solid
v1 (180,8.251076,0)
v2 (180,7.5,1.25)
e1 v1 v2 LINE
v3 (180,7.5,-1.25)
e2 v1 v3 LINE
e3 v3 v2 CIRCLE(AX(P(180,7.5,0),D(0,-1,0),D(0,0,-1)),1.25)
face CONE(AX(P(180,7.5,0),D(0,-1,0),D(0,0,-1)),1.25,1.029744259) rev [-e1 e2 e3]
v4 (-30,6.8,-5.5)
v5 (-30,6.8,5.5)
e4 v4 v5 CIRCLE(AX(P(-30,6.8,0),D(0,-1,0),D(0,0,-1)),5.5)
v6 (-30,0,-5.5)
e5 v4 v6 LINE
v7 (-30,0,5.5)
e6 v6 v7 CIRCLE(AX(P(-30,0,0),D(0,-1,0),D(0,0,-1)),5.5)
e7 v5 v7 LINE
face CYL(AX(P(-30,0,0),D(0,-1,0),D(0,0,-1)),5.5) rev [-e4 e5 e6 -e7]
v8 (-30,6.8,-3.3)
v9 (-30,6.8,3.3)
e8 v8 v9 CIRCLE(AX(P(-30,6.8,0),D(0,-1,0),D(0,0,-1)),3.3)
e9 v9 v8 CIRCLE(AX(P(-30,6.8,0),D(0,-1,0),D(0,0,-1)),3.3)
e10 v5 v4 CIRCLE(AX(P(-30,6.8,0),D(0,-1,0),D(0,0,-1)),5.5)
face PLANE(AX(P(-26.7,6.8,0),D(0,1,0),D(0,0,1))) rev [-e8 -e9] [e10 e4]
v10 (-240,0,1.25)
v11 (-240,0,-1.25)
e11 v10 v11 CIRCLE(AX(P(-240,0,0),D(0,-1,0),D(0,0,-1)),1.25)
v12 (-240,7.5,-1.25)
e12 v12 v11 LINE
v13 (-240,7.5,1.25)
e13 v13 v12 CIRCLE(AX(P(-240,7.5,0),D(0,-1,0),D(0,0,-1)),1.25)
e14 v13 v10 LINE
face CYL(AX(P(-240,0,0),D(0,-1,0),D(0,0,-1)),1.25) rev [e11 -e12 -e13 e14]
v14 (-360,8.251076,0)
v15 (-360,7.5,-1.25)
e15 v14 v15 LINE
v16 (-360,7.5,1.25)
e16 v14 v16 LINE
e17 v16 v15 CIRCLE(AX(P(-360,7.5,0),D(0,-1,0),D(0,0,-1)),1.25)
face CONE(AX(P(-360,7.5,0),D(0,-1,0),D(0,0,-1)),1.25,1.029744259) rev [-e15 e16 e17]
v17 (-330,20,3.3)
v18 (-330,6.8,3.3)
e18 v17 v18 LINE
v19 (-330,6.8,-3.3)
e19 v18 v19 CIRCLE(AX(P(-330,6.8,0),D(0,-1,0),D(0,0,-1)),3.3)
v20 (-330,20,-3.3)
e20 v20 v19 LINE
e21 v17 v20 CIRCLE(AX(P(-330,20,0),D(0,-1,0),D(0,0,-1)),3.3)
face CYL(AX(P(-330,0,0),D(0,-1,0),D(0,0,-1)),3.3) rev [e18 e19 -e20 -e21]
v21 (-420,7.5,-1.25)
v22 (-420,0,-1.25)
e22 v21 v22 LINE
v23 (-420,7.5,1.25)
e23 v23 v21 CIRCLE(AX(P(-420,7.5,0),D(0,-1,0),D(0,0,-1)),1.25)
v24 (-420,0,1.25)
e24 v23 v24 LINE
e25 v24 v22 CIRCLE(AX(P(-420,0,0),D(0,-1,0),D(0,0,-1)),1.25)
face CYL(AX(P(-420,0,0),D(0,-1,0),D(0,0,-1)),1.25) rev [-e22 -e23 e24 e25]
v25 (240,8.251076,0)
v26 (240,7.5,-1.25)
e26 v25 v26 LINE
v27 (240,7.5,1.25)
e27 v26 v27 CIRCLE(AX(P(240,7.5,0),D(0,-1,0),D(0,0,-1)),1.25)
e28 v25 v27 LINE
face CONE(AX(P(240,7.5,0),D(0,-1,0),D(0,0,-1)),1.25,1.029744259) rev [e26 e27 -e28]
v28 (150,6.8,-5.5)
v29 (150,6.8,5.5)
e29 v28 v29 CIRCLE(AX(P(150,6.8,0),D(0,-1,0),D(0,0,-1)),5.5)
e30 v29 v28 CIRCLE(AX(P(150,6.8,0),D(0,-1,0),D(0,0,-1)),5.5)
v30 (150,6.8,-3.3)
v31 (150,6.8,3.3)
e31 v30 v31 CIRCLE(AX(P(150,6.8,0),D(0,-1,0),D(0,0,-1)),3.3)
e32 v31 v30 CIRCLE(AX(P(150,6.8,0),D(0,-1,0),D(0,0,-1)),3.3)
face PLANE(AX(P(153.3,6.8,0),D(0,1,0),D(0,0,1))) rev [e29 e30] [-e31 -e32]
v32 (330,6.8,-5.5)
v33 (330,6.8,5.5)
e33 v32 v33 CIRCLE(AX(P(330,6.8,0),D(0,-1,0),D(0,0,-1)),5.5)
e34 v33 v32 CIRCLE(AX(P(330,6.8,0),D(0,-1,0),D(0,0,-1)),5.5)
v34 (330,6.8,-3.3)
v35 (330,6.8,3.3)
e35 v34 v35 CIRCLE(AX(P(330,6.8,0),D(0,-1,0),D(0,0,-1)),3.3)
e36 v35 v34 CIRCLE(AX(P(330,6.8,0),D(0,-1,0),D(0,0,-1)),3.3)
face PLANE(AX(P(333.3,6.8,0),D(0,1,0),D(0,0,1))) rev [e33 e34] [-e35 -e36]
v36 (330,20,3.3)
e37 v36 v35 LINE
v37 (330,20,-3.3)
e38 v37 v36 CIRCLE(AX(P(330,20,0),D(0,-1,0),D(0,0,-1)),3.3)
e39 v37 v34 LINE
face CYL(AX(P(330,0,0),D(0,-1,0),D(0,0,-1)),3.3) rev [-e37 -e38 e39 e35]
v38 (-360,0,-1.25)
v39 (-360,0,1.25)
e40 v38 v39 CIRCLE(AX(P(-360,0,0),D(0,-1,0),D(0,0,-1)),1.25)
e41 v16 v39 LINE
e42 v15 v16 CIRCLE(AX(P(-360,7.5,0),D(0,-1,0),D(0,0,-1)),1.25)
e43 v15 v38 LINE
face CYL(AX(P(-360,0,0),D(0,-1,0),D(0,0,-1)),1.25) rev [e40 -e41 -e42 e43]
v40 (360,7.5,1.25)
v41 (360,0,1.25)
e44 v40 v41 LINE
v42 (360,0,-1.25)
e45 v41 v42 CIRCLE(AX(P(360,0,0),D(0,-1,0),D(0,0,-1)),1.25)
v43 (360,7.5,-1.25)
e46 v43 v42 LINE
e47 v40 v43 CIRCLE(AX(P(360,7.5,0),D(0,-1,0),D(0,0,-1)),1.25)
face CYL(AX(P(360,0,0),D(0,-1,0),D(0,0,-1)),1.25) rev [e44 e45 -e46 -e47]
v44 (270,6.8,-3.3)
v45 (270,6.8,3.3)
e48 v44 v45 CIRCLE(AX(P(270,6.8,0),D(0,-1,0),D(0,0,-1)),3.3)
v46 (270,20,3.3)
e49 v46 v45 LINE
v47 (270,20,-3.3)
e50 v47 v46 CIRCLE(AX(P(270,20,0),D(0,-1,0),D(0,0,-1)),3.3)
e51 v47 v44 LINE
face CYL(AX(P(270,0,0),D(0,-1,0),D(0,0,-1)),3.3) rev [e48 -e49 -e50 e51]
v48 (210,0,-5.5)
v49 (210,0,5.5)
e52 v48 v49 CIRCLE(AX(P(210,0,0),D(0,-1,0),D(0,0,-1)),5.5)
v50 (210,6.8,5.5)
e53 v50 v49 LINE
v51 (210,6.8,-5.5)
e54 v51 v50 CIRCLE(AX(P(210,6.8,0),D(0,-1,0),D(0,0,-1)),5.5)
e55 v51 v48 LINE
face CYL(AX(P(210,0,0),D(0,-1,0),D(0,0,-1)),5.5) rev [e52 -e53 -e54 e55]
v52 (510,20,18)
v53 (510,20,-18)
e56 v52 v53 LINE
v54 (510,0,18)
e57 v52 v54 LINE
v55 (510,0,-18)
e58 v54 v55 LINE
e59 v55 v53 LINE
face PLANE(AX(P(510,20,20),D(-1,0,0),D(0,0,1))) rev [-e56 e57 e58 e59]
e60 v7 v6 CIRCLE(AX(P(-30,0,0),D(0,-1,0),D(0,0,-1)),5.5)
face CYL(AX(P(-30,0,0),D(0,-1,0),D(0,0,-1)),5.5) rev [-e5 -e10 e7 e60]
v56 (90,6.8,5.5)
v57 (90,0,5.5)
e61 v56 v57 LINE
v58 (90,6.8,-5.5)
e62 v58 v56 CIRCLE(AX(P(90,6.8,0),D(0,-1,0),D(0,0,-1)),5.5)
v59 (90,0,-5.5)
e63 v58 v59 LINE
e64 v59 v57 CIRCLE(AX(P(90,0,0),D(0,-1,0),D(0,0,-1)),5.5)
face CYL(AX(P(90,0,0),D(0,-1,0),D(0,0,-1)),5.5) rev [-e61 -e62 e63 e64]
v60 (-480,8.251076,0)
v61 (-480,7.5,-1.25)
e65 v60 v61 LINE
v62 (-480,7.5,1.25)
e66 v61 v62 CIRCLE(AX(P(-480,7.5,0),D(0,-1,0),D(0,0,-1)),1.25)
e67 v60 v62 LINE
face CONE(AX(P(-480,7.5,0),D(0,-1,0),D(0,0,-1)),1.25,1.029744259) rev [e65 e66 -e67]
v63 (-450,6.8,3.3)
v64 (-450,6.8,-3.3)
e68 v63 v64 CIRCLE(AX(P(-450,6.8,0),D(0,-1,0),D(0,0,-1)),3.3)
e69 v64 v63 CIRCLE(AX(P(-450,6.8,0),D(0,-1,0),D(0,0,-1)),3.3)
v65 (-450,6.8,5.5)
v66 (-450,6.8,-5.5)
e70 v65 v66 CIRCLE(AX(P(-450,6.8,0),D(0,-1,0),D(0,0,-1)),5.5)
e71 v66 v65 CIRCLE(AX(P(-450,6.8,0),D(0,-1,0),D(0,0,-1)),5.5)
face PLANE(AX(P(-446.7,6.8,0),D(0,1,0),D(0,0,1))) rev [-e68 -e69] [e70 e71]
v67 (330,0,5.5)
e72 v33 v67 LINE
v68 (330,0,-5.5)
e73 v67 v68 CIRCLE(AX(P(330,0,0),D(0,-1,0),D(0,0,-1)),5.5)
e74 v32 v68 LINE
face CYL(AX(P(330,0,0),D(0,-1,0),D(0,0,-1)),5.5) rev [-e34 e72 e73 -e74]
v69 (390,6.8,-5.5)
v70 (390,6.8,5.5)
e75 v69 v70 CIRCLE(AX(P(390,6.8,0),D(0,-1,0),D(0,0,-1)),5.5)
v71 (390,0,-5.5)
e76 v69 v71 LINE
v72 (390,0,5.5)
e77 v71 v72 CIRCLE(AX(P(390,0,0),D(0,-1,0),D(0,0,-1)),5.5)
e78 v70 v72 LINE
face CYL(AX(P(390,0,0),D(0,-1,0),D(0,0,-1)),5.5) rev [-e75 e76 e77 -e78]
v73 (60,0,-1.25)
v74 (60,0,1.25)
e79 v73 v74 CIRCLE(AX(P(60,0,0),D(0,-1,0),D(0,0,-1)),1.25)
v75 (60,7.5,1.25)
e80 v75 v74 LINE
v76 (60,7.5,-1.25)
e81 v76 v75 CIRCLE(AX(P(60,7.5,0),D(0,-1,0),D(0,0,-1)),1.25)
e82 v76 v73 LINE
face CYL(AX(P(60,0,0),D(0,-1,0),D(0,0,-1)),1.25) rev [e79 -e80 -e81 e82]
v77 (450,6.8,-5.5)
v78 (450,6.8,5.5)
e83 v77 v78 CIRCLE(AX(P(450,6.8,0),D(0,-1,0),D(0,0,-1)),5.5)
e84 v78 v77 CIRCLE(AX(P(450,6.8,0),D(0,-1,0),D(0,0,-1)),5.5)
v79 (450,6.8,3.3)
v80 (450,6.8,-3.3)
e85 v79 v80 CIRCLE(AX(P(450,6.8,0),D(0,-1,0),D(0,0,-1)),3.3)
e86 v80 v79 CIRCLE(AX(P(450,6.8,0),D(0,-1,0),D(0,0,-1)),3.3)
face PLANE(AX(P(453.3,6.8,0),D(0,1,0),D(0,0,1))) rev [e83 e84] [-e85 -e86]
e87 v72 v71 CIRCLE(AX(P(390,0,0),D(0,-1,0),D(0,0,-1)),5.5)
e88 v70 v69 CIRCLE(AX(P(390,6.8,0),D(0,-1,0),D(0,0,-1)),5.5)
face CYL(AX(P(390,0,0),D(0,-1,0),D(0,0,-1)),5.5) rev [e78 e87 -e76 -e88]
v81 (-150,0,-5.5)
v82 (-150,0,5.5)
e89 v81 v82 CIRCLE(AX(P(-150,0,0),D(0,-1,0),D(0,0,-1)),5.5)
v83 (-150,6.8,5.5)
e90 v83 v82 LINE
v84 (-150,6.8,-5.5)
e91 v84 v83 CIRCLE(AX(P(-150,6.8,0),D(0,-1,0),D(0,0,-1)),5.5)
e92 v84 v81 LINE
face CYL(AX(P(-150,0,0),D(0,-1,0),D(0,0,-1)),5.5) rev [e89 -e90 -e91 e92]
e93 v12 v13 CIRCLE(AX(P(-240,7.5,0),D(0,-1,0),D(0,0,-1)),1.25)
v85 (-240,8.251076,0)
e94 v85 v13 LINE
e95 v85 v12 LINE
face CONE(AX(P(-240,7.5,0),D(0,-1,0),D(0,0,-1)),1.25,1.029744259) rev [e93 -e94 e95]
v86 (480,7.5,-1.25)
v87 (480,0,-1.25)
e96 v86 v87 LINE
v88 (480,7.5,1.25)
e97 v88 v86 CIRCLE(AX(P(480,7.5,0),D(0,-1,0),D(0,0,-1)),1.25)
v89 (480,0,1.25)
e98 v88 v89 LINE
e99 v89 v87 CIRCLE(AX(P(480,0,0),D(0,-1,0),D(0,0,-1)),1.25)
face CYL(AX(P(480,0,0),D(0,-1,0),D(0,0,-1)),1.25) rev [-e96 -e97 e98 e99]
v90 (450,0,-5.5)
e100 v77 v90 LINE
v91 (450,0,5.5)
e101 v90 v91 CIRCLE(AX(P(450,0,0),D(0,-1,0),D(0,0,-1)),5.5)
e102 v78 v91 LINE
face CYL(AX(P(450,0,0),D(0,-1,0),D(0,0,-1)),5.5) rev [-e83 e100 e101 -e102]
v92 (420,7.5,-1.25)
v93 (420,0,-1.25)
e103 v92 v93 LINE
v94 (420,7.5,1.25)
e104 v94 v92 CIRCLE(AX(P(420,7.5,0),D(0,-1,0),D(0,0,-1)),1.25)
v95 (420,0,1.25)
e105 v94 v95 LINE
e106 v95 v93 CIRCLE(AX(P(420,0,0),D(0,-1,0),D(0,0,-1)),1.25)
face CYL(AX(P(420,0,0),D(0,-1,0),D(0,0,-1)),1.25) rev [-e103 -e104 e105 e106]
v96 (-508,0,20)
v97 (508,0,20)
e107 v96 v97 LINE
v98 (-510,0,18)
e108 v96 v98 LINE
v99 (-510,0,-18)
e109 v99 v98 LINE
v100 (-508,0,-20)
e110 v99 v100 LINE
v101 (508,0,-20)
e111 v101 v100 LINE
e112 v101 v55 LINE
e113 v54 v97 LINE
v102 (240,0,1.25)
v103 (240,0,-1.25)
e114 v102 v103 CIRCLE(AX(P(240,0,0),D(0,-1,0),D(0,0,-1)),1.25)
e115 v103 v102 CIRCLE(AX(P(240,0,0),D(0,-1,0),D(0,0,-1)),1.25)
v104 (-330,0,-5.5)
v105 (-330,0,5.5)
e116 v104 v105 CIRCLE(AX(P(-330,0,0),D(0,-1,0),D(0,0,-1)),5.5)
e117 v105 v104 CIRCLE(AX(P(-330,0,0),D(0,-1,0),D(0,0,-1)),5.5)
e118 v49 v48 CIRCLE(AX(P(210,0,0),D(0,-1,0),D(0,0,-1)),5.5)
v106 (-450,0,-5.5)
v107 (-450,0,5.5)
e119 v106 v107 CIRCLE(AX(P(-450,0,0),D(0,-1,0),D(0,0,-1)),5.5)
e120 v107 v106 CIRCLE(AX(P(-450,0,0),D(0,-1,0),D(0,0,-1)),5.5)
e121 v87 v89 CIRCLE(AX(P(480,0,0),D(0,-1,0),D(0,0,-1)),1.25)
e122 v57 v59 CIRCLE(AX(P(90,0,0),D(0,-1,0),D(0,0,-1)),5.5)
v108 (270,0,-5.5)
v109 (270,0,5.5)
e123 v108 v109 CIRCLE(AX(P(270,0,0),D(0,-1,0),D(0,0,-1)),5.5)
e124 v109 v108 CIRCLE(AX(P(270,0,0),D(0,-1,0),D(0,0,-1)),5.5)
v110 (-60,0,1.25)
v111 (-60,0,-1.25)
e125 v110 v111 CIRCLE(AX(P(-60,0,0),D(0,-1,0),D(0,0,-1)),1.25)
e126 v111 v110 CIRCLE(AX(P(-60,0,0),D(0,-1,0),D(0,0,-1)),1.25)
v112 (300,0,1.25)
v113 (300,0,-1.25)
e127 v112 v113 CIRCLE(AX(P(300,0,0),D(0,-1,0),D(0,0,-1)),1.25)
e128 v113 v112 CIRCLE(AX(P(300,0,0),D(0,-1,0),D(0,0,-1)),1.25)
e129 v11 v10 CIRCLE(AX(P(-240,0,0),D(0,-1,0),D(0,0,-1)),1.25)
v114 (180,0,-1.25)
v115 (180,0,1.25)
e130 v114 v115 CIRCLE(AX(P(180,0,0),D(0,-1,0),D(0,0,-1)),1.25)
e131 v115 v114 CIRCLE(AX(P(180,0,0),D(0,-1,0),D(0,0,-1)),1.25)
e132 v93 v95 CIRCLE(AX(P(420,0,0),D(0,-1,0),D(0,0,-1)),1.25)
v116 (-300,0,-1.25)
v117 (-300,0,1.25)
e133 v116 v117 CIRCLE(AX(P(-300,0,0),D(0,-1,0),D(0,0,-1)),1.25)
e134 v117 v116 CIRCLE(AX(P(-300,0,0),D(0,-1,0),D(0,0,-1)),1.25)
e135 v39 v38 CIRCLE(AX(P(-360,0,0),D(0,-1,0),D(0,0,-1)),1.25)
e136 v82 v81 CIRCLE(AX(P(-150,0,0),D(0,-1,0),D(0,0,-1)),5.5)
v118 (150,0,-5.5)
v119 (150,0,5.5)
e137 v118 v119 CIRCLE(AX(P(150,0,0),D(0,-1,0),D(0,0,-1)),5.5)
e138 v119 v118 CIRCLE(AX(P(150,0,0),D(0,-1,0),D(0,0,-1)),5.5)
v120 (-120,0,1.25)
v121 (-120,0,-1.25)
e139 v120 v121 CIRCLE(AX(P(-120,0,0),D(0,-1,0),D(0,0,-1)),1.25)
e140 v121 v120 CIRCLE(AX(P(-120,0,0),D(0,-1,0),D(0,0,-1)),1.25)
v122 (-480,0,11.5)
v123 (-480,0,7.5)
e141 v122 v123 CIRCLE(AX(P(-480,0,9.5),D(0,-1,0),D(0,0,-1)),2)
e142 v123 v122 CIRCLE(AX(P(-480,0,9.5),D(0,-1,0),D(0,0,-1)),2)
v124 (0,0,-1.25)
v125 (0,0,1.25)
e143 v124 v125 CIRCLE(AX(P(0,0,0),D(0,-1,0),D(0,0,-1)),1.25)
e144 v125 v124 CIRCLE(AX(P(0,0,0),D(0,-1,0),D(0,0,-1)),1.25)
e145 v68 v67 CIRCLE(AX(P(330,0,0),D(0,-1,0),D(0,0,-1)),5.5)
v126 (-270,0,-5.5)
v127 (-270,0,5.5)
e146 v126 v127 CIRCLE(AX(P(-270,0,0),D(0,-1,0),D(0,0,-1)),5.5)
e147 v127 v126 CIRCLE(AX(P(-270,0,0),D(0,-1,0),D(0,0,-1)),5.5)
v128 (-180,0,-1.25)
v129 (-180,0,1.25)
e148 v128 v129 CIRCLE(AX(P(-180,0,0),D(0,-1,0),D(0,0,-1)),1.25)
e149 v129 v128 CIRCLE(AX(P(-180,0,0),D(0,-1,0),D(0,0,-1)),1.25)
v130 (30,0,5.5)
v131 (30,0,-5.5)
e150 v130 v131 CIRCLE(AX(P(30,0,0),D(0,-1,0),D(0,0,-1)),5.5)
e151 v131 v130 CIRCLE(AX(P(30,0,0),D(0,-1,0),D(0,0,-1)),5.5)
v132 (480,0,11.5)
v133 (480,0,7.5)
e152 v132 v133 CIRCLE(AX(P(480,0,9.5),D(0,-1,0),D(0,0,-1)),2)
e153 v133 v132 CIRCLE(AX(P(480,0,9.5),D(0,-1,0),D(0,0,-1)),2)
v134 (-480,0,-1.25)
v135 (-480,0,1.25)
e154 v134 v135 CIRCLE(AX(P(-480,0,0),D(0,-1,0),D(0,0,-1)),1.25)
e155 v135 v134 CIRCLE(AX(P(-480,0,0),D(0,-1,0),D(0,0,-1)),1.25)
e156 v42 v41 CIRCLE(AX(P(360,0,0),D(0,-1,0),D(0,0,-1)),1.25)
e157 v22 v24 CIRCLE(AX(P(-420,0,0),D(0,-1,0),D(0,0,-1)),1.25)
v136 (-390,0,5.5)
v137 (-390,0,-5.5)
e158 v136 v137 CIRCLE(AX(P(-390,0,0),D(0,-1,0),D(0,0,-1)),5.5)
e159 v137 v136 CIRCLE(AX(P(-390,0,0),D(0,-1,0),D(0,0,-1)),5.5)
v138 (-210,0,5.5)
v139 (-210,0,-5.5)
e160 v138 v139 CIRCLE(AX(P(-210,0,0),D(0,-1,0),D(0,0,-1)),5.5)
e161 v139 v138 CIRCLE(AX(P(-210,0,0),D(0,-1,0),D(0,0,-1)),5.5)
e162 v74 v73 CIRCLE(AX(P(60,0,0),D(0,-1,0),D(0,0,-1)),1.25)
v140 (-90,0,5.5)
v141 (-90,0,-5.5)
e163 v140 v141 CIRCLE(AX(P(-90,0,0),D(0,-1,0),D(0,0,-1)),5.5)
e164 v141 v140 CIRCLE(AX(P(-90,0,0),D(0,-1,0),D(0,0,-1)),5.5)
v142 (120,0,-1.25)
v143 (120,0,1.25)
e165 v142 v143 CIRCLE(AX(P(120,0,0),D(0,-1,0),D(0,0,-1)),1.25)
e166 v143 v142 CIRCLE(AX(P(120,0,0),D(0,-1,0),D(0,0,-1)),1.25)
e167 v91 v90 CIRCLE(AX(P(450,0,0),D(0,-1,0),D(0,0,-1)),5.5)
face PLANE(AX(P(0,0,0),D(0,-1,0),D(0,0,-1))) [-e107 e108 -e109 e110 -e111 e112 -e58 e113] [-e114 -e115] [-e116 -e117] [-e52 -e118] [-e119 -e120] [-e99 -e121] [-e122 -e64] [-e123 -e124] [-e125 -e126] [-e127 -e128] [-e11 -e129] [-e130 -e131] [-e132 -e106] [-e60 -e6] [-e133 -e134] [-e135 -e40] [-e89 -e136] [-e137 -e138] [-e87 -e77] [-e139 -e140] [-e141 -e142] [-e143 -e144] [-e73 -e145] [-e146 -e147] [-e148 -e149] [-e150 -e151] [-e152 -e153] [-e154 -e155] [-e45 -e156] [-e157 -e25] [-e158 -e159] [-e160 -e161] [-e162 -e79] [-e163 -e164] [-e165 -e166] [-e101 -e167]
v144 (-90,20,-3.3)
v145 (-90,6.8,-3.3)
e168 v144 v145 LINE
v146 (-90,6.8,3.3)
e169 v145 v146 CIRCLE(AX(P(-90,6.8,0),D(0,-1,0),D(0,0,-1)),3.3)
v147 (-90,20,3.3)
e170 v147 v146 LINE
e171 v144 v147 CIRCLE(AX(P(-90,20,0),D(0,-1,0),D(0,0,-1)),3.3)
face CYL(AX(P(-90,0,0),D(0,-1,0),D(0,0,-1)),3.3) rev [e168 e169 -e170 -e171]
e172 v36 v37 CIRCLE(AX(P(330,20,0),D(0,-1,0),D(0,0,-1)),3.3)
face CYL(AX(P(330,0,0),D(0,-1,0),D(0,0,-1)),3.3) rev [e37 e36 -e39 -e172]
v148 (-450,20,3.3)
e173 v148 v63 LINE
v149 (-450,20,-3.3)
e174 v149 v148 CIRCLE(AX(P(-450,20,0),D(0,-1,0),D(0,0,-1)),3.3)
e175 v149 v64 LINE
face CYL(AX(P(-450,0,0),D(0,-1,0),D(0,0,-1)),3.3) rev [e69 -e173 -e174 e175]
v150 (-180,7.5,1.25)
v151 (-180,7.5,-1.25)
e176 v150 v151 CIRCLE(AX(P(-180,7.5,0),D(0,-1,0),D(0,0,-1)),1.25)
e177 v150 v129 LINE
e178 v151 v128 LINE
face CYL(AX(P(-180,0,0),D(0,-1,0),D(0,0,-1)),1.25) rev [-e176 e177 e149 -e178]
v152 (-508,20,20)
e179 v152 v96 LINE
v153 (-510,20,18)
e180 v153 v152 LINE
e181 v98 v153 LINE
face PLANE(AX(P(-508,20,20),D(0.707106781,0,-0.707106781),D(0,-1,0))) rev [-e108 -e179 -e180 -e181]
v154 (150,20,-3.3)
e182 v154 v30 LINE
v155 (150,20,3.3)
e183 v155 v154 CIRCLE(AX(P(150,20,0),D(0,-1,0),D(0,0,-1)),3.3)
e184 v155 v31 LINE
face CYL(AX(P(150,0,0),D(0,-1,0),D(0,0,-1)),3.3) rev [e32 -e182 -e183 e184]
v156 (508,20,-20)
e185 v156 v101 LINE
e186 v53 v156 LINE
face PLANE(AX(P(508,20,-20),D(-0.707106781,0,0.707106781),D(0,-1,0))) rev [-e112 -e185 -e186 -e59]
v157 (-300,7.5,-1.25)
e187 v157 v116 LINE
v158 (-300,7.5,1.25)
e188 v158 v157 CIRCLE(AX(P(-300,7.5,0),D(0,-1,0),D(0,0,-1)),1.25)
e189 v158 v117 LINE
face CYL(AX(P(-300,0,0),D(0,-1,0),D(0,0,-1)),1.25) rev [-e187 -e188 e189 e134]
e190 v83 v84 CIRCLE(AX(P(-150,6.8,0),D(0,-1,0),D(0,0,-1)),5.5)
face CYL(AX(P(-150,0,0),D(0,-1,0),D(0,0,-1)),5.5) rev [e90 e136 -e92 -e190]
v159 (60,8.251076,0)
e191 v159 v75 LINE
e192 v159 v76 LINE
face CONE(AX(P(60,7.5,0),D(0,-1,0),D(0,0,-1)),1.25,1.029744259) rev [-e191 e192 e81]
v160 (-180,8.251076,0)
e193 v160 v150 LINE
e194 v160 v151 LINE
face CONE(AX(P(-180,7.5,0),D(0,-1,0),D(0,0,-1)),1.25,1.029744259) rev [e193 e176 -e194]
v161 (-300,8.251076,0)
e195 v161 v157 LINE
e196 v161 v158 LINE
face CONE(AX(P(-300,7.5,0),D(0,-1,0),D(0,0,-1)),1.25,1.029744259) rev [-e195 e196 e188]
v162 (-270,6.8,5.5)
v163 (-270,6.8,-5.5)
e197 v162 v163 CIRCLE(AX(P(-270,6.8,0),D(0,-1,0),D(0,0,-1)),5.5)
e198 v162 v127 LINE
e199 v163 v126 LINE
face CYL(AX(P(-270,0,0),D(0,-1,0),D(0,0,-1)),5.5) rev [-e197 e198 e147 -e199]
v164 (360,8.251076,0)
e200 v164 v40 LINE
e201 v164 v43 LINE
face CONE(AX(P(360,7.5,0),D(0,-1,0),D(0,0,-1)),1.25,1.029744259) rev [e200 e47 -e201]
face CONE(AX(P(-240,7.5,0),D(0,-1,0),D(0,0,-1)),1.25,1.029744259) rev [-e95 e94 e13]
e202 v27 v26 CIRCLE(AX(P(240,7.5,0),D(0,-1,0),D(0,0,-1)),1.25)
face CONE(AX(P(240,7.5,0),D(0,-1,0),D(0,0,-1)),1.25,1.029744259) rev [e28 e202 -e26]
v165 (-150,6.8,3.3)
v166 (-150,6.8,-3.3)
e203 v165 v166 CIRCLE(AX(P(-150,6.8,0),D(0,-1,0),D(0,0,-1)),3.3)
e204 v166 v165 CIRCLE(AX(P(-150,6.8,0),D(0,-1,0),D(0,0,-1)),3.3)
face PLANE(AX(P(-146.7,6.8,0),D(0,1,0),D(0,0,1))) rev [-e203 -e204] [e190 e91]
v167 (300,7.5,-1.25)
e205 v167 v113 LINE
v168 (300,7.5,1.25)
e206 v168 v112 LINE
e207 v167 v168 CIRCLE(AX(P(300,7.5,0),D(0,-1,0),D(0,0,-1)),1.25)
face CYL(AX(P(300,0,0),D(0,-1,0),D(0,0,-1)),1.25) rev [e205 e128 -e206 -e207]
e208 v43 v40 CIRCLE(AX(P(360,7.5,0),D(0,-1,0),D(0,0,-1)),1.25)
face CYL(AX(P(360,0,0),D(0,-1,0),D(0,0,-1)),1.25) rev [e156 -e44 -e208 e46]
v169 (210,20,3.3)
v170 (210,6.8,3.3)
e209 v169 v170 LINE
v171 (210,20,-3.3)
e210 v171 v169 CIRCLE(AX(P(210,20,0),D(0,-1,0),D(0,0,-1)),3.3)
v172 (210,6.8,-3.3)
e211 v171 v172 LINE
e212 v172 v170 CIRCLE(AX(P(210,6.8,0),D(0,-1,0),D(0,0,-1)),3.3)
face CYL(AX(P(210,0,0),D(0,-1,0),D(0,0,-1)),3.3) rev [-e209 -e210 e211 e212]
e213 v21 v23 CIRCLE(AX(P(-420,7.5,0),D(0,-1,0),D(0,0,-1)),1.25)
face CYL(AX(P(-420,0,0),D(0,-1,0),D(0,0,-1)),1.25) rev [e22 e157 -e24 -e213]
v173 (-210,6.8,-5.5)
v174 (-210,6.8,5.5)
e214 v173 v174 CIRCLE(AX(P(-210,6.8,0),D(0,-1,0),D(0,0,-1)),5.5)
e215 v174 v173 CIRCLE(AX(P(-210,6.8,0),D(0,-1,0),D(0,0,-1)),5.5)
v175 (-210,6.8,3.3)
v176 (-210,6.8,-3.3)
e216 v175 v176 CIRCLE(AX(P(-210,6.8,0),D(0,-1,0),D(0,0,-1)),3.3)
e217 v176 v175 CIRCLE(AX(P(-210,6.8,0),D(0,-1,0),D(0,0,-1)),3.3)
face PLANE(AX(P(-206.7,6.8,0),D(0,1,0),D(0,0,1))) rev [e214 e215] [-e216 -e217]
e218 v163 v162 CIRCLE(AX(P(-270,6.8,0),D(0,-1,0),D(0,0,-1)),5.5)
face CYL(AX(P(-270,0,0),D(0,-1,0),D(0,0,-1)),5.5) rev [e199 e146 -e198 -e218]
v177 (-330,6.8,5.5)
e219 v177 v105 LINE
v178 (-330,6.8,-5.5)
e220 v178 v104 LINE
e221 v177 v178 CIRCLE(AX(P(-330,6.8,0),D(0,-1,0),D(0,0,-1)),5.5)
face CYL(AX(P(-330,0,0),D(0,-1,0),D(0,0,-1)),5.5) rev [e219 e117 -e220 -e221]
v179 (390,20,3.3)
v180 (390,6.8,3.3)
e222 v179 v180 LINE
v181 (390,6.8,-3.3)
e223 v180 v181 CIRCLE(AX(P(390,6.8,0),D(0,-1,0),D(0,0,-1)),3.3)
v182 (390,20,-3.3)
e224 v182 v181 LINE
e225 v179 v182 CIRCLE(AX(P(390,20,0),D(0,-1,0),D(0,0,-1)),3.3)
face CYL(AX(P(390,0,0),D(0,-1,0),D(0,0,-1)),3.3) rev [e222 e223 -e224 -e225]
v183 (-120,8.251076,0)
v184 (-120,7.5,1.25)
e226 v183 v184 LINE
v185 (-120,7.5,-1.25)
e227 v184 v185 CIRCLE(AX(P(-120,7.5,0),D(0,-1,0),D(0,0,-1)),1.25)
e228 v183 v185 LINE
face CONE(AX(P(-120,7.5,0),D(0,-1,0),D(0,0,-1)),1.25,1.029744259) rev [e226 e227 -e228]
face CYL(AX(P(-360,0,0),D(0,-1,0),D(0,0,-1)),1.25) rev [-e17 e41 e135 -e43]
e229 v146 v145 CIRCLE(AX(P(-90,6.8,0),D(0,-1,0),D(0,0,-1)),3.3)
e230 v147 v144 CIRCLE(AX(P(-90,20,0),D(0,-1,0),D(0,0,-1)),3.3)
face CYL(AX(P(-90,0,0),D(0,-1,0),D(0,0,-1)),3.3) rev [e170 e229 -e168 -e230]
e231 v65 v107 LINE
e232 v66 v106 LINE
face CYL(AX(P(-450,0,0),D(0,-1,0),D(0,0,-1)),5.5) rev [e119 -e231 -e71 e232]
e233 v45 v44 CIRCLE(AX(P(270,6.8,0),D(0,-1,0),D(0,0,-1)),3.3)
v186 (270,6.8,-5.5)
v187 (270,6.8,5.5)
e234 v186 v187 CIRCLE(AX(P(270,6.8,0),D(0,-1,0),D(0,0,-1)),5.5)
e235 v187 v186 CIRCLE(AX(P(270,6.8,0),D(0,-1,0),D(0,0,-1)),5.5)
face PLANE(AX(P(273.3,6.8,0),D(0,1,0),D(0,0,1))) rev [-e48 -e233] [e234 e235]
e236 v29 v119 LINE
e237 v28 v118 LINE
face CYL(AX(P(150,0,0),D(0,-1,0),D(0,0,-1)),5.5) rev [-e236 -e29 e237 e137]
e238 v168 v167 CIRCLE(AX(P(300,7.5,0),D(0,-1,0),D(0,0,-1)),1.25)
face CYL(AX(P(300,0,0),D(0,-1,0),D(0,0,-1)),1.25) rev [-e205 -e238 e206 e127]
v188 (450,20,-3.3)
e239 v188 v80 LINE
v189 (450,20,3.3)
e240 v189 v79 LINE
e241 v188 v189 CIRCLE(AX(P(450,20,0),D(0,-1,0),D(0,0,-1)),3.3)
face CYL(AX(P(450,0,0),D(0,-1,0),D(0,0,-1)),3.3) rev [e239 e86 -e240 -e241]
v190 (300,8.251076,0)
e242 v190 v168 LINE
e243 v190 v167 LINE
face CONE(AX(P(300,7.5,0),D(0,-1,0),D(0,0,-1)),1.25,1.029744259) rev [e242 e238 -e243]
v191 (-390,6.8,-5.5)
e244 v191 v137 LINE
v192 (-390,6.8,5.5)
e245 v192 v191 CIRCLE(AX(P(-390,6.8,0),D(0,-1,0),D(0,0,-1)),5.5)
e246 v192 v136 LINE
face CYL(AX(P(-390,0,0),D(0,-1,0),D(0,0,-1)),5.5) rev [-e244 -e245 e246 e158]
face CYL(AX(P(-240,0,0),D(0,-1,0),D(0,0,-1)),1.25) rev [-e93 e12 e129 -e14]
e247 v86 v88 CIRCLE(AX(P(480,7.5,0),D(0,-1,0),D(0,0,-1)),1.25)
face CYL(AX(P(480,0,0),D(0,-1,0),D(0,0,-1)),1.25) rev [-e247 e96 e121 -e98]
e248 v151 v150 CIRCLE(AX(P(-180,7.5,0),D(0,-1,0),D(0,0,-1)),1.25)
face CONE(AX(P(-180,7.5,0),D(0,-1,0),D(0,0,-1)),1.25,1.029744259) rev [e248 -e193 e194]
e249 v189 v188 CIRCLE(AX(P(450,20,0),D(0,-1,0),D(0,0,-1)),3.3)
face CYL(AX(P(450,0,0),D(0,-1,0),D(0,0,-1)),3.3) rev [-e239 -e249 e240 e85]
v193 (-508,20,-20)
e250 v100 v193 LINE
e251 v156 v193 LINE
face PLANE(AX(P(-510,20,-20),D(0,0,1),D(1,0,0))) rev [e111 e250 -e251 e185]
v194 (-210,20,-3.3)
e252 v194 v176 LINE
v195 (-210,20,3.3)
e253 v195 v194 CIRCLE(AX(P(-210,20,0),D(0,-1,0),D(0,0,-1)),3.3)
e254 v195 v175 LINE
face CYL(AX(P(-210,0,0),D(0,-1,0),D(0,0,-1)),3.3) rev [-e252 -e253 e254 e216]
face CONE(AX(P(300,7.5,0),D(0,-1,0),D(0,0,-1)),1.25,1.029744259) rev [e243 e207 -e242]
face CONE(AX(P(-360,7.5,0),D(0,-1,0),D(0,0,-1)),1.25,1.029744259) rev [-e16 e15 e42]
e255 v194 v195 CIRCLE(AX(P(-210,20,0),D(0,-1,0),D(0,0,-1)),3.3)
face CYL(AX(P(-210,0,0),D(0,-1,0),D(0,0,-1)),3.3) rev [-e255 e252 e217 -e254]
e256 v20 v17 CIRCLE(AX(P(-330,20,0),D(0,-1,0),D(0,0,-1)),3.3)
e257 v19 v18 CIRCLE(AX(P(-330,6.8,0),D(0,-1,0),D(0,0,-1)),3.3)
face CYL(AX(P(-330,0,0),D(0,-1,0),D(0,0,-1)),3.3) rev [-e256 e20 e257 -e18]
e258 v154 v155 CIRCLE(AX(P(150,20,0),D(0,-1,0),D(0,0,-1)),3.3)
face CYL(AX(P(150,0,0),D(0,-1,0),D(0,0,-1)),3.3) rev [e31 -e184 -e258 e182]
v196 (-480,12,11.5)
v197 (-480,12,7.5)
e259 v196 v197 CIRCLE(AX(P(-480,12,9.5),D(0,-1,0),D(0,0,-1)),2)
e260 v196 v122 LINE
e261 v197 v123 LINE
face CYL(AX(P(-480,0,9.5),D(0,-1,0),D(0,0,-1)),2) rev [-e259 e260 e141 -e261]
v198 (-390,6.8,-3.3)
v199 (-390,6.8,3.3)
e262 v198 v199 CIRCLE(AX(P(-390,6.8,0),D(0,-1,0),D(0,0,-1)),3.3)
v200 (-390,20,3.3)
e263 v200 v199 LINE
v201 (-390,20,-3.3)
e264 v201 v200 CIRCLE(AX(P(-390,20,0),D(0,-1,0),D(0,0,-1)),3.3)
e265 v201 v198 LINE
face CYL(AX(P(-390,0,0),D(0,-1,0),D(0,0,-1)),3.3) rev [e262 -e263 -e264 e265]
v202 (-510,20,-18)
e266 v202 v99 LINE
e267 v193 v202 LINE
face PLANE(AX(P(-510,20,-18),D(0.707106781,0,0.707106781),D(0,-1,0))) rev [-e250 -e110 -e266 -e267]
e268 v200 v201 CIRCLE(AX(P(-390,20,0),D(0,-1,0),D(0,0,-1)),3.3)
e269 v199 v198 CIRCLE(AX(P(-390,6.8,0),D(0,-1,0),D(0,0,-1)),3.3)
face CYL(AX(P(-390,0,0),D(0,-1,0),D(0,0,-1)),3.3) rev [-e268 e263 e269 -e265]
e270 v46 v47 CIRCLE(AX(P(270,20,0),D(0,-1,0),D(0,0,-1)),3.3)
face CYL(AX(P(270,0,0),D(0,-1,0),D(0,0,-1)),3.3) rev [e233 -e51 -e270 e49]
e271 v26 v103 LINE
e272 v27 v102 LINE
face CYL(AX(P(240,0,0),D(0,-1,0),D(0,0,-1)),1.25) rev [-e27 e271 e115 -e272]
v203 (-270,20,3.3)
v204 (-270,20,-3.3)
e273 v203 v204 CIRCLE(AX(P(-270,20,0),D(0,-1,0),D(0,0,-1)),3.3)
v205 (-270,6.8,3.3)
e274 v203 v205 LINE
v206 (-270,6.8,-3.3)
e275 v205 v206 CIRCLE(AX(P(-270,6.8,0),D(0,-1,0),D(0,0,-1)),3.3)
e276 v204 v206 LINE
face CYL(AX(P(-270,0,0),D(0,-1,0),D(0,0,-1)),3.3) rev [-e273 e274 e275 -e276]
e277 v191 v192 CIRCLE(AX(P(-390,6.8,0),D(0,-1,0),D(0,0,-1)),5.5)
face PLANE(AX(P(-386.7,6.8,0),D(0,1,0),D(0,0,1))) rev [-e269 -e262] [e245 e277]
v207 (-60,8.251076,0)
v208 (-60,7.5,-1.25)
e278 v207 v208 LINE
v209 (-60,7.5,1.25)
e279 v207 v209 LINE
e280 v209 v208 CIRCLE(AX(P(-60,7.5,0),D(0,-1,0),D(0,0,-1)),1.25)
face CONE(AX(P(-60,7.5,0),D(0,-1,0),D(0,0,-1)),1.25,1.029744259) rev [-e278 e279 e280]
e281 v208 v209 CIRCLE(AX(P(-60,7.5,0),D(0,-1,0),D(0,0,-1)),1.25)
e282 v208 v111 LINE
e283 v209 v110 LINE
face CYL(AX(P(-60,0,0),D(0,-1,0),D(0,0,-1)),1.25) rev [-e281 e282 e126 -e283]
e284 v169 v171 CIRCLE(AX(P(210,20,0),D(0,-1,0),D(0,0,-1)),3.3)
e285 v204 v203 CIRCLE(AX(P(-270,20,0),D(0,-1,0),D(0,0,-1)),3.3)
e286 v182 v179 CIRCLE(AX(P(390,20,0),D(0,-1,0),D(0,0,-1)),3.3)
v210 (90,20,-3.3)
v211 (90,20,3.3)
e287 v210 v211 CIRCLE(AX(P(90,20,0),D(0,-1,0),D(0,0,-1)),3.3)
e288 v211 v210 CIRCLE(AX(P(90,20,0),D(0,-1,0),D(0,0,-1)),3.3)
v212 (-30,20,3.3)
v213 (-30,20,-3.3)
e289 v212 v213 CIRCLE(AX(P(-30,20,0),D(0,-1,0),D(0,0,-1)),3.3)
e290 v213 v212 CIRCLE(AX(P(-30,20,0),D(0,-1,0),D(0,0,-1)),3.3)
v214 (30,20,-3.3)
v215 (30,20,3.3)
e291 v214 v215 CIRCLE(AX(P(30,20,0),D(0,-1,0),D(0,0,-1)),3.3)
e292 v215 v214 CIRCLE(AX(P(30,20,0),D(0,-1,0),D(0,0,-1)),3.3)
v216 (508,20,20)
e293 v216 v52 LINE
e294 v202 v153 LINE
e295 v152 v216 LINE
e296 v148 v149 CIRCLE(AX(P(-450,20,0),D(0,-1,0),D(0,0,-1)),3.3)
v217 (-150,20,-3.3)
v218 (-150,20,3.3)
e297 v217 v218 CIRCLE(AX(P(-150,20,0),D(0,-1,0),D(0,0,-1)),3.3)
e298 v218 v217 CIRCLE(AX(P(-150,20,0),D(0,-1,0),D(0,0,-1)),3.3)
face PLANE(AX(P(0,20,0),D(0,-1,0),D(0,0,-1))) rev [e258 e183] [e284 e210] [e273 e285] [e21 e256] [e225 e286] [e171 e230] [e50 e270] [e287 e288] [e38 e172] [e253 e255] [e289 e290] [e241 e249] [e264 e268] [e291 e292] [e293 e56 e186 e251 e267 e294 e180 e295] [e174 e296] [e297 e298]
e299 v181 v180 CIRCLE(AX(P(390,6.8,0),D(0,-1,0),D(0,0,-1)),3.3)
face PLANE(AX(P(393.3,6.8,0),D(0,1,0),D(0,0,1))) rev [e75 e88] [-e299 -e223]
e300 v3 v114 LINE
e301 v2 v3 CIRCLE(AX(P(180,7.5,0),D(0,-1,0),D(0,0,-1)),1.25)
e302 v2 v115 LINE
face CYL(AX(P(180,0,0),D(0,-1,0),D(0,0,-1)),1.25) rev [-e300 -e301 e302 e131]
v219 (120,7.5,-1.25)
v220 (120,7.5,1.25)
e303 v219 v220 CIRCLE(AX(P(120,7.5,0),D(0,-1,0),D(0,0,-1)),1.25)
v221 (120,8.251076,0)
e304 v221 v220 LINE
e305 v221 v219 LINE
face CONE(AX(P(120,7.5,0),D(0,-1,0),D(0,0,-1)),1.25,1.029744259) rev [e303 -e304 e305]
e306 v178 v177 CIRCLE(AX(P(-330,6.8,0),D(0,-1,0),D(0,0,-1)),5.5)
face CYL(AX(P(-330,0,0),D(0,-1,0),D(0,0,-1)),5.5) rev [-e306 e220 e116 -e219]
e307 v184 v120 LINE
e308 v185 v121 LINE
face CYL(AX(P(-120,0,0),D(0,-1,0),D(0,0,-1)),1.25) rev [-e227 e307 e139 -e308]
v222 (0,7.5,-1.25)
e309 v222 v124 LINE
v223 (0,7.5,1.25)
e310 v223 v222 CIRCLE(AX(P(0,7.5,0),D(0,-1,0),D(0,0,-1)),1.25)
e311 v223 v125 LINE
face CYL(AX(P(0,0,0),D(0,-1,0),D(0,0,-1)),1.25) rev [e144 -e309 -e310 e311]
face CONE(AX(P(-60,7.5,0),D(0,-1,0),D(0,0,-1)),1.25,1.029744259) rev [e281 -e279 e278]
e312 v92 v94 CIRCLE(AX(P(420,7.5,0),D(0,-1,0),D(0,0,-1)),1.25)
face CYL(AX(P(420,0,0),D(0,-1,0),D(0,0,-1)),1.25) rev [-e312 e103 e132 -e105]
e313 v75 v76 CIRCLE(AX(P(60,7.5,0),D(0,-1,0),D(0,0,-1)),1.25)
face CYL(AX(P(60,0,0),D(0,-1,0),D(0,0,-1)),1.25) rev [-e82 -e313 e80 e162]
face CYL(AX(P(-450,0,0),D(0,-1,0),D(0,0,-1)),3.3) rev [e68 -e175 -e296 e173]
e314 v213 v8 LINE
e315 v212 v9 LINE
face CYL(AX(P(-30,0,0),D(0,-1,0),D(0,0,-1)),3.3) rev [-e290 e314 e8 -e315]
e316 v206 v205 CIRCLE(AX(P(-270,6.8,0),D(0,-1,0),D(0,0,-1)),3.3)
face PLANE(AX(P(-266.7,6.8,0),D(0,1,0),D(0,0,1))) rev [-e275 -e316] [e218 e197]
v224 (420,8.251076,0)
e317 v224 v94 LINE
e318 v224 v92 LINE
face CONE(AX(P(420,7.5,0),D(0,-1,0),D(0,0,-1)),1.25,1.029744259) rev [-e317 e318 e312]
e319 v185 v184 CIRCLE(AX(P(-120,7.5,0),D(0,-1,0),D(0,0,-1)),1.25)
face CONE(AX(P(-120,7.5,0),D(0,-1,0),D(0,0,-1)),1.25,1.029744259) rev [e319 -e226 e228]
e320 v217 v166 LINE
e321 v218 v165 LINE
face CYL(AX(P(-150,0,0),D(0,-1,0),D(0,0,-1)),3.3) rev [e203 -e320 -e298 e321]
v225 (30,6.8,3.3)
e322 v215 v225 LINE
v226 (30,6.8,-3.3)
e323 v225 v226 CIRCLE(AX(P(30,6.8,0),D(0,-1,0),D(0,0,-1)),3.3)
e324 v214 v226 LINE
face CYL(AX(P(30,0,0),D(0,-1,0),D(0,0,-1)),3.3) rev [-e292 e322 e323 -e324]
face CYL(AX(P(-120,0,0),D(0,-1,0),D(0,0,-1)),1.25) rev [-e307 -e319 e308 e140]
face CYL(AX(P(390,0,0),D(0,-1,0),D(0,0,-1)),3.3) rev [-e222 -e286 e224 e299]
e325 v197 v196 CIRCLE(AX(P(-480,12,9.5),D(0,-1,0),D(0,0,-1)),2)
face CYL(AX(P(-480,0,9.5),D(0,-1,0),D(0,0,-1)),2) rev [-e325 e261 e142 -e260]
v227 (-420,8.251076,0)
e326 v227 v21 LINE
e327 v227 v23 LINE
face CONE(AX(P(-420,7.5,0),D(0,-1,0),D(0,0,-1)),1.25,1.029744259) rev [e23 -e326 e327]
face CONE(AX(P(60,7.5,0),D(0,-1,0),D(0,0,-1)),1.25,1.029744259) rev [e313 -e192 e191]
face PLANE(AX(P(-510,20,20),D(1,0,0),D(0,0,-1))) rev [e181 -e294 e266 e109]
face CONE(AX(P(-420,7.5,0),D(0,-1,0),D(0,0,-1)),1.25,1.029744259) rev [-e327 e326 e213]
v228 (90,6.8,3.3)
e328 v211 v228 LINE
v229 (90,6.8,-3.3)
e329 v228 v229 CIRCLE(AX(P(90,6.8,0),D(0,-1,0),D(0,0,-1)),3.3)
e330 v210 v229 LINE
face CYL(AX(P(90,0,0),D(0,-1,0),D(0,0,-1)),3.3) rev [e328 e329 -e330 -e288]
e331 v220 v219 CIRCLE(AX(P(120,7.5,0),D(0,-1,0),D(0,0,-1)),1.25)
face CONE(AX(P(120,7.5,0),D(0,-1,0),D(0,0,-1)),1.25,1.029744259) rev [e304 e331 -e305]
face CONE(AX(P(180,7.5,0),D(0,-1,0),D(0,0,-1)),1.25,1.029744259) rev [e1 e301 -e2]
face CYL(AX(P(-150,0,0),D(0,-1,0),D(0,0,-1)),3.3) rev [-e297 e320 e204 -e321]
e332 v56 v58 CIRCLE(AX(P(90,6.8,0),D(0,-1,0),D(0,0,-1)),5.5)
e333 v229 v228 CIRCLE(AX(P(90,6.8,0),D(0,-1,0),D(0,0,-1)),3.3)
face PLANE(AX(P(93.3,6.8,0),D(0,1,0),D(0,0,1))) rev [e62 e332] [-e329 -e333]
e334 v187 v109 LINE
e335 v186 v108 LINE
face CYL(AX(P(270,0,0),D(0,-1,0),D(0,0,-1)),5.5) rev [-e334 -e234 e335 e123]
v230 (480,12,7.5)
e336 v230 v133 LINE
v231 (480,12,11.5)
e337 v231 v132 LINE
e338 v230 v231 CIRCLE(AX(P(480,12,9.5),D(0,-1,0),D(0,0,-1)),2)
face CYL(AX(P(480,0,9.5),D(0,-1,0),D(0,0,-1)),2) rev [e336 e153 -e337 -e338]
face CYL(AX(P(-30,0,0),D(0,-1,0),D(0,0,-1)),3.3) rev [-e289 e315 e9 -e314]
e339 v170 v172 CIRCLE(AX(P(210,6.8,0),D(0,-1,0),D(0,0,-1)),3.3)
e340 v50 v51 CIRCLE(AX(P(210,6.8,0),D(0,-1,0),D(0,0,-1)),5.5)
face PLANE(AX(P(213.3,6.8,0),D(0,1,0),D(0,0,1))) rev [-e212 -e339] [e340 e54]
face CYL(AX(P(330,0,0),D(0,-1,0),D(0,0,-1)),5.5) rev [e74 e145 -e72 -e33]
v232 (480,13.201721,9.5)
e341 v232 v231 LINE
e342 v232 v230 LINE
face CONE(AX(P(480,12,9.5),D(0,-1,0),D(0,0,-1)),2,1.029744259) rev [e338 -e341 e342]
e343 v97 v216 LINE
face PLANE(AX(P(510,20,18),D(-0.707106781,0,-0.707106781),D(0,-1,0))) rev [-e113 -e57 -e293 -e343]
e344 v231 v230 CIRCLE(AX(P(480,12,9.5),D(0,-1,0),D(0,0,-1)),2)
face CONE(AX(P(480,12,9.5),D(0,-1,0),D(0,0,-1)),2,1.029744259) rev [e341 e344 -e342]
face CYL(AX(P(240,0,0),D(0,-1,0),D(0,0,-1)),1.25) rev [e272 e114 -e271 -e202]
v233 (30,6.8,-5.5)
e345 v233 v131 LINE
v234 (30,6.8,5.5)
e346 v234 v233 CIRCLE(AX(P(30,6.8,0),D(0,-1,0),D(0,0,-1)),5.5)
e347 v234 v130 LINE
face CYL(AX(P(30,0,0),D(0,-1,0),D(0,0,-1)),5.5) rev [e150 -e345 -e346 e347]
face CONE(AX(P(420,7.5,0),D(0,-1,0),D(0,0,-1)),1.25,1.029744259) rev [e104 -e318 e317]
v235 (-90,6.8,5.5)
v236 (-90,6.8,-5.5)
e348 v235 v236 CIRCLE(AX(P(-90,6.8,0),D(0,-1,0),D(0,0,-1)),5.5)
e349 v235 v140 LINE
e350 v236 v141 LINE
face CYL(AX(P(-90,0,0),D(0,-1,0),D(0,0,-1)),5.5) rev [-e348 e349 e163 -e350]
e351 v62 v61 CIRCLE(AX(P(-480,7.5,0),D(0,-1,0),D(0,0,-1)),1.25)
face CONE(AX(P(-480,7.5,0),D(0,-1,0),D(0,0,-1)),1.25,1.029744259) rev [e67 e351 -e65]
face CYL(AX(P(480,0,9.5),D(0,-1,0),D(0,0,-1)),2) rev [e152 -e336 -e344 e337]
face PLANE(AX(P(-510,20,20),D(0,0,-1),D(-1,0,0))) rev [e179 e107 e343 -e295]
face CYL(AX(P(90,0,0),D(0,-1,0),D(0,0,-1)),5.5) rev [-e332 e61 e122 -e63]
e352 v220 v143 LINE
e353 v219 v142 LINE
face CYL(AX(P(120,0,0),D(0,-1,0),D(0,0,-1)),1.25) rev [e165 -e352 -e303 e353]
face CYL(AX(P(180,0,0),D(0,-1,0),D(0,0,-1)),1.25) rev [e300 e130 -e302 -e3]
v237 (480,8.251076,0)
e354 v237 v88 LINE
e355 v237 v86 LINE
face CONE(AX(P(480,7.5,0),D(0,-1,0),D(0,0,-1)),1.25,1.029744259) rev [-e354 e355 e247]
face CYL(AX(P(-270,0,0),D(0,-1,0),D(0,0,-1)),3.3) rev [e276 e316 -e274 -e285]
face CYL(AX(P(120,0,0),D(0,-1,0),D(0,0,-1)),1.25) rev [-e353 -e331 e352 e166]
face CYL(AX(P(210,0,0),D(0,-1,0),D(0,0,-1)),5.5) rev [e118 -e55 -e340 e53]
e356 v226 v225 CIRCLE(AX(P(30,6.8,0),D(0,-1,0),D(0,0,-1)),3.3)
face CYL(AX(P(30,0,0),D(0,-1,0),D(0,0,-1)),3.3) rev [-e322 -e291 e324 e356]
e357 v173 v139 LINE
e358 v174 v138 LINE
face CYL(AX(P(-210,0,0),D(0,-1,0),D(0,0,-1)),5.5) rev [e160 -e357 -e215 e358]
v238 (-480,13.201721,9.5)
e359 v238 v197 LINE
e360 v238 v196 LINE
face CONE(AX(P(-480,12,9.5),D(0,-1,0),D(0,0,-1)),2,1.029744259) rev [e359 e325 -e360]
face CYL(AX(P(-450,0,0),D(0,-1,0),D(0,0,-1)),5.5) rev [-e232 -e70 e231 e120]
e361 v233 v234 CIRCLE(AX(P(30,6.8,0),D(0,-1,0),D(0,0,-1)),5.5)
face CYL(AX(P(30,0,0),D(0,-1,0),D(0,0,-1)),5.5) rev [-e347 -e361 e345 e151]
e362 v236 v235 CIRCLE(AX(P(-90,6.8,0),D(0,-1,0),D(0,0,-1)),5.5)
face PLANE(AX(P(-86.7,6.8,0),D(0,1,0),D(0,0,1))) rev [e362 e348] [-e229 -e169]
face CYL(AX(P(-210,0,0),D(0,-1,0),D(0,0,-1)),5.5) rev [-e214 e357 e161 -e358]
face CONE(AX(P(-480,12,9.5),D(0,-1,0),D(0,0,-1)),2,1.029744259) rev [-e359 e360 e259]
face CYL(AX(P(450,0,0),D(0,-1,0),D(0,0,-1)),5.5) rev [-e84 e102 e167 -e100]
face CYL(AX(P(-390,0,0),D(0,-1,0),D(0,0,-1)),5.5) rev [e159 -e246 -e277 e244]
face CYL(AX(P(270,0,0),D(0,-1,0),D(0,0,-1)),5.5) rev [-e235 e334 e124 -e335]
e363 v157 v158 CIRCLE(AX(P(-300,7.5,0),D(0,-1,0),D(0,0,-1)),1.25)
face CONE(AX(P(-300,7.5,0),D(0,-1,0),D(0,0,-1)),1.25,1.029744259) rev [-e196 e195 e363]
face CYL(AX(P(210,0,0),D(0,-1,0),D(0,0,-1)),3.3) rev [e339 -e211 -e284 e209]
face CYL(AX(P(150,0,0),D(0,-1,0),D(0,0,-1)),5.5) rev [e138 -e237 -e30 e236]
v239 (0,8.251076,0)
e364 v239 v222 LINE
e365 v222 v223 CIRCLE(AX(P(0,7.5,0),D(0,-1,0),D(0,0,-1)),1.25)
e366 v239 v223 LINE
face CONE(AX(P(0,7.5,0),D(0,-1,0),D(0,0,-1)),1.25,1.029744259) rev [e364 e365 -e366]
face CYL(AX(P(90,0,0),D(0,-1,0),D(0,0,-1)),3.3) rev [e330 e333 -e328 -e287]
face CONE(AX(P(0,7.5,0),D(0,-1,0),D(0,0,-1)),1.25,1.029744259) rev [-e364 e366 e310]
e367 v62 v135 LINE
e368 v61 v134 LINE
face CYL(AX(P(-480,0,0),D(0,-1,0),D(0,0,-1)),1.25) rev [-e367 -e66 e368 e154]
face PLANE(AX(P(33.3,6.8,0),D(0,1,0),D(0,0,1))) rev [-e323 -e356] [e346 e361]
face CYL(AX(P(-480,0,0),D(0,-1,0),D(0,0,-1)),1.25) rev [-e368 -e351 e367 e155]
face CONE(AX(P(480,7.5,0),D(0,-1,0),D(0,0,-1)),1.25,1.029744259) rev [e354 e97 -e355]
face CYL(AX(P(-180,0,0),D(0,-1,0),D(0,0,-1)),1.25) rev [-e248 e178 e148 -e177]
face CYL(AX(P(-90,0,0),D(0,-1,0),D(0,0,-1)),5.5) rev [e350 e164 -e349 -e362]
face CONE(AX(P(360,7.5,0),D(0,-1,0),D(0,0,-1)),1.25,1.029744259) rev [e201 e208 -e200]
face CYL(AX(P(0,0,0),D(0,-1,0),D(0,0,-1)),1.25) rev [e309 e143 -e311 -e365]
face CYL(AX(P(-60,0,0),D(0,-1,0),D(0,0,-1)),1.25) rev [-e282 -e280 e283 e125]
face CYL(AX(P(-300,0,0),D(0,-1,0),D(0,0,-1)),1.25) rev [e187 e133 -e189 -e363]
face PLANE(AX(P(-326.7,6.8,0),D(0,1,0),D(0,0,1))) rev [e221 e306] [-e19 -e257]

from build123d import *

# Parameters (mm, degrees)
SKETCH_1_W                   = 1020
SKETCH_1_H                   = 40
EXTRUDE_1_DEPTH              = 20
CHAMFER_1_SIZE               = 2
F_4_0MM_1_D                  = 4
F_4_0MM_1_DEPTH              = 12
F_4_0MM_1_TIP                = 1.201721238
PATTERN_LINEAR_5_COUNT       = 17
PATTERN_LINEAR_5_PITCH       = 60
HOLE_WIZARD_M6_1_D           = 6.6
HOLE_WIZARD_M6_1_CBORE_D     = 11
HOLE_WIZARD_M6_1_CBORE_DEPTH = 6.8
PATTERN_LINEAR_6_COUNT       = 16
PATTERN_LINEAR_6_PITCH       = 60


with BuildPart() as part:
    # 草图1 → 凸台-拉伸1 (new body)
    with BuildSketch(Plane(origin=(0, 0, 0), x_dir=(1, 0, 0), z_dir=(0, 1, 0))):
        Rectangle(SKETCH_1_W, SKETCH_1_H)
    extrude(amount=EXTRUDE_1_DEPTH)

    # 倒角1
    chamfer_1_edges = [part.edges().sort_by_distance(p)[0] for p in [
        (510, 10, 20),
        (-510, 10, 20),
        (-510, 10, -20),
        (510, 10, -20),
    ]]
    chamfer(chamfer_1_edges, length=CHAMFER_1_SIZE)

    # Ø4.0mm 暗销孔1
    with Locations(Plane(origin=(0, 0, 0), x_dir=(-1, 0, 0), z_dir=(0, -1, 0))):
        with Locations((480, -9.5), (-480, -9.5)):
            Hole(F_4_0MM_1_D / 2, depth=F_4_0MM_1_DEPTH)
            with Locations((0, 0, -(F_4_0MM_1_DEPTH + F_4_0MM_1_TIP / 2))):  # 118° drill point
                Cone(0, F_4_0MM_1_D / 2, F_4_0MM_1_TIP, mode=Mode.SUBTRACT)

    # 草图9 → M3 螺纹孔1 (revolve, cut)
    with BuildSketch(Plane(origin=(480, 0, 0), x_dir=(0, 0, -1), z_dir=(1, 0, 0))):
        Polygon((0, 0), (0, 8.251075774), (1.25, 7.5), (1.25, 0), align=None)
    hole_wizard_m3_1 = revolve(axis=Axis((480, -6.35, 0), (0, 1, 0)), mode=Mode.SUBTRACT)

    # 阵列(线性)5: M3 螺纹孔1 ×17
    with Locations(*[(-i * PATTERN_LINEAR_5_PITCH, 0, 0) for i in range(1, PATTERN_LINEAR_5_COUNT)]):
        add(hole_wizard_m3_1, mode=Mode.SUBTRACT)

    # M6 六角圆柱头螺钉的柱形沉头孔1 (through all)
    with Locations(Plane(origin=(0, 0, 0), x_dir=(-1, 0, 0), z_dir=(0, -1, 0))):
        with Locations((-450, 0)):
            hole_wizard_m6_1 = CounterBoreHole(HOLE_WIZARD_M6_1_D / 2, HOLE_WIZARD_M6_1_CBORE_D / 2, HOLE_WIZARD_M6_1_CBORE_DEPTH)

    # 阵列(线性)6: M6 六角圆柱头螺钉的柱形沉头孔1 ×16
    with Locations(*[(-i * PATTERN_LINEAR_6_PITCH, 0, 0) for i in range(1, PATTERN_LINEAR_6_COUNT)]):
        add(hole_wizard_m6_1, mode=Mode.SUBTRACT)


solid = part.part
